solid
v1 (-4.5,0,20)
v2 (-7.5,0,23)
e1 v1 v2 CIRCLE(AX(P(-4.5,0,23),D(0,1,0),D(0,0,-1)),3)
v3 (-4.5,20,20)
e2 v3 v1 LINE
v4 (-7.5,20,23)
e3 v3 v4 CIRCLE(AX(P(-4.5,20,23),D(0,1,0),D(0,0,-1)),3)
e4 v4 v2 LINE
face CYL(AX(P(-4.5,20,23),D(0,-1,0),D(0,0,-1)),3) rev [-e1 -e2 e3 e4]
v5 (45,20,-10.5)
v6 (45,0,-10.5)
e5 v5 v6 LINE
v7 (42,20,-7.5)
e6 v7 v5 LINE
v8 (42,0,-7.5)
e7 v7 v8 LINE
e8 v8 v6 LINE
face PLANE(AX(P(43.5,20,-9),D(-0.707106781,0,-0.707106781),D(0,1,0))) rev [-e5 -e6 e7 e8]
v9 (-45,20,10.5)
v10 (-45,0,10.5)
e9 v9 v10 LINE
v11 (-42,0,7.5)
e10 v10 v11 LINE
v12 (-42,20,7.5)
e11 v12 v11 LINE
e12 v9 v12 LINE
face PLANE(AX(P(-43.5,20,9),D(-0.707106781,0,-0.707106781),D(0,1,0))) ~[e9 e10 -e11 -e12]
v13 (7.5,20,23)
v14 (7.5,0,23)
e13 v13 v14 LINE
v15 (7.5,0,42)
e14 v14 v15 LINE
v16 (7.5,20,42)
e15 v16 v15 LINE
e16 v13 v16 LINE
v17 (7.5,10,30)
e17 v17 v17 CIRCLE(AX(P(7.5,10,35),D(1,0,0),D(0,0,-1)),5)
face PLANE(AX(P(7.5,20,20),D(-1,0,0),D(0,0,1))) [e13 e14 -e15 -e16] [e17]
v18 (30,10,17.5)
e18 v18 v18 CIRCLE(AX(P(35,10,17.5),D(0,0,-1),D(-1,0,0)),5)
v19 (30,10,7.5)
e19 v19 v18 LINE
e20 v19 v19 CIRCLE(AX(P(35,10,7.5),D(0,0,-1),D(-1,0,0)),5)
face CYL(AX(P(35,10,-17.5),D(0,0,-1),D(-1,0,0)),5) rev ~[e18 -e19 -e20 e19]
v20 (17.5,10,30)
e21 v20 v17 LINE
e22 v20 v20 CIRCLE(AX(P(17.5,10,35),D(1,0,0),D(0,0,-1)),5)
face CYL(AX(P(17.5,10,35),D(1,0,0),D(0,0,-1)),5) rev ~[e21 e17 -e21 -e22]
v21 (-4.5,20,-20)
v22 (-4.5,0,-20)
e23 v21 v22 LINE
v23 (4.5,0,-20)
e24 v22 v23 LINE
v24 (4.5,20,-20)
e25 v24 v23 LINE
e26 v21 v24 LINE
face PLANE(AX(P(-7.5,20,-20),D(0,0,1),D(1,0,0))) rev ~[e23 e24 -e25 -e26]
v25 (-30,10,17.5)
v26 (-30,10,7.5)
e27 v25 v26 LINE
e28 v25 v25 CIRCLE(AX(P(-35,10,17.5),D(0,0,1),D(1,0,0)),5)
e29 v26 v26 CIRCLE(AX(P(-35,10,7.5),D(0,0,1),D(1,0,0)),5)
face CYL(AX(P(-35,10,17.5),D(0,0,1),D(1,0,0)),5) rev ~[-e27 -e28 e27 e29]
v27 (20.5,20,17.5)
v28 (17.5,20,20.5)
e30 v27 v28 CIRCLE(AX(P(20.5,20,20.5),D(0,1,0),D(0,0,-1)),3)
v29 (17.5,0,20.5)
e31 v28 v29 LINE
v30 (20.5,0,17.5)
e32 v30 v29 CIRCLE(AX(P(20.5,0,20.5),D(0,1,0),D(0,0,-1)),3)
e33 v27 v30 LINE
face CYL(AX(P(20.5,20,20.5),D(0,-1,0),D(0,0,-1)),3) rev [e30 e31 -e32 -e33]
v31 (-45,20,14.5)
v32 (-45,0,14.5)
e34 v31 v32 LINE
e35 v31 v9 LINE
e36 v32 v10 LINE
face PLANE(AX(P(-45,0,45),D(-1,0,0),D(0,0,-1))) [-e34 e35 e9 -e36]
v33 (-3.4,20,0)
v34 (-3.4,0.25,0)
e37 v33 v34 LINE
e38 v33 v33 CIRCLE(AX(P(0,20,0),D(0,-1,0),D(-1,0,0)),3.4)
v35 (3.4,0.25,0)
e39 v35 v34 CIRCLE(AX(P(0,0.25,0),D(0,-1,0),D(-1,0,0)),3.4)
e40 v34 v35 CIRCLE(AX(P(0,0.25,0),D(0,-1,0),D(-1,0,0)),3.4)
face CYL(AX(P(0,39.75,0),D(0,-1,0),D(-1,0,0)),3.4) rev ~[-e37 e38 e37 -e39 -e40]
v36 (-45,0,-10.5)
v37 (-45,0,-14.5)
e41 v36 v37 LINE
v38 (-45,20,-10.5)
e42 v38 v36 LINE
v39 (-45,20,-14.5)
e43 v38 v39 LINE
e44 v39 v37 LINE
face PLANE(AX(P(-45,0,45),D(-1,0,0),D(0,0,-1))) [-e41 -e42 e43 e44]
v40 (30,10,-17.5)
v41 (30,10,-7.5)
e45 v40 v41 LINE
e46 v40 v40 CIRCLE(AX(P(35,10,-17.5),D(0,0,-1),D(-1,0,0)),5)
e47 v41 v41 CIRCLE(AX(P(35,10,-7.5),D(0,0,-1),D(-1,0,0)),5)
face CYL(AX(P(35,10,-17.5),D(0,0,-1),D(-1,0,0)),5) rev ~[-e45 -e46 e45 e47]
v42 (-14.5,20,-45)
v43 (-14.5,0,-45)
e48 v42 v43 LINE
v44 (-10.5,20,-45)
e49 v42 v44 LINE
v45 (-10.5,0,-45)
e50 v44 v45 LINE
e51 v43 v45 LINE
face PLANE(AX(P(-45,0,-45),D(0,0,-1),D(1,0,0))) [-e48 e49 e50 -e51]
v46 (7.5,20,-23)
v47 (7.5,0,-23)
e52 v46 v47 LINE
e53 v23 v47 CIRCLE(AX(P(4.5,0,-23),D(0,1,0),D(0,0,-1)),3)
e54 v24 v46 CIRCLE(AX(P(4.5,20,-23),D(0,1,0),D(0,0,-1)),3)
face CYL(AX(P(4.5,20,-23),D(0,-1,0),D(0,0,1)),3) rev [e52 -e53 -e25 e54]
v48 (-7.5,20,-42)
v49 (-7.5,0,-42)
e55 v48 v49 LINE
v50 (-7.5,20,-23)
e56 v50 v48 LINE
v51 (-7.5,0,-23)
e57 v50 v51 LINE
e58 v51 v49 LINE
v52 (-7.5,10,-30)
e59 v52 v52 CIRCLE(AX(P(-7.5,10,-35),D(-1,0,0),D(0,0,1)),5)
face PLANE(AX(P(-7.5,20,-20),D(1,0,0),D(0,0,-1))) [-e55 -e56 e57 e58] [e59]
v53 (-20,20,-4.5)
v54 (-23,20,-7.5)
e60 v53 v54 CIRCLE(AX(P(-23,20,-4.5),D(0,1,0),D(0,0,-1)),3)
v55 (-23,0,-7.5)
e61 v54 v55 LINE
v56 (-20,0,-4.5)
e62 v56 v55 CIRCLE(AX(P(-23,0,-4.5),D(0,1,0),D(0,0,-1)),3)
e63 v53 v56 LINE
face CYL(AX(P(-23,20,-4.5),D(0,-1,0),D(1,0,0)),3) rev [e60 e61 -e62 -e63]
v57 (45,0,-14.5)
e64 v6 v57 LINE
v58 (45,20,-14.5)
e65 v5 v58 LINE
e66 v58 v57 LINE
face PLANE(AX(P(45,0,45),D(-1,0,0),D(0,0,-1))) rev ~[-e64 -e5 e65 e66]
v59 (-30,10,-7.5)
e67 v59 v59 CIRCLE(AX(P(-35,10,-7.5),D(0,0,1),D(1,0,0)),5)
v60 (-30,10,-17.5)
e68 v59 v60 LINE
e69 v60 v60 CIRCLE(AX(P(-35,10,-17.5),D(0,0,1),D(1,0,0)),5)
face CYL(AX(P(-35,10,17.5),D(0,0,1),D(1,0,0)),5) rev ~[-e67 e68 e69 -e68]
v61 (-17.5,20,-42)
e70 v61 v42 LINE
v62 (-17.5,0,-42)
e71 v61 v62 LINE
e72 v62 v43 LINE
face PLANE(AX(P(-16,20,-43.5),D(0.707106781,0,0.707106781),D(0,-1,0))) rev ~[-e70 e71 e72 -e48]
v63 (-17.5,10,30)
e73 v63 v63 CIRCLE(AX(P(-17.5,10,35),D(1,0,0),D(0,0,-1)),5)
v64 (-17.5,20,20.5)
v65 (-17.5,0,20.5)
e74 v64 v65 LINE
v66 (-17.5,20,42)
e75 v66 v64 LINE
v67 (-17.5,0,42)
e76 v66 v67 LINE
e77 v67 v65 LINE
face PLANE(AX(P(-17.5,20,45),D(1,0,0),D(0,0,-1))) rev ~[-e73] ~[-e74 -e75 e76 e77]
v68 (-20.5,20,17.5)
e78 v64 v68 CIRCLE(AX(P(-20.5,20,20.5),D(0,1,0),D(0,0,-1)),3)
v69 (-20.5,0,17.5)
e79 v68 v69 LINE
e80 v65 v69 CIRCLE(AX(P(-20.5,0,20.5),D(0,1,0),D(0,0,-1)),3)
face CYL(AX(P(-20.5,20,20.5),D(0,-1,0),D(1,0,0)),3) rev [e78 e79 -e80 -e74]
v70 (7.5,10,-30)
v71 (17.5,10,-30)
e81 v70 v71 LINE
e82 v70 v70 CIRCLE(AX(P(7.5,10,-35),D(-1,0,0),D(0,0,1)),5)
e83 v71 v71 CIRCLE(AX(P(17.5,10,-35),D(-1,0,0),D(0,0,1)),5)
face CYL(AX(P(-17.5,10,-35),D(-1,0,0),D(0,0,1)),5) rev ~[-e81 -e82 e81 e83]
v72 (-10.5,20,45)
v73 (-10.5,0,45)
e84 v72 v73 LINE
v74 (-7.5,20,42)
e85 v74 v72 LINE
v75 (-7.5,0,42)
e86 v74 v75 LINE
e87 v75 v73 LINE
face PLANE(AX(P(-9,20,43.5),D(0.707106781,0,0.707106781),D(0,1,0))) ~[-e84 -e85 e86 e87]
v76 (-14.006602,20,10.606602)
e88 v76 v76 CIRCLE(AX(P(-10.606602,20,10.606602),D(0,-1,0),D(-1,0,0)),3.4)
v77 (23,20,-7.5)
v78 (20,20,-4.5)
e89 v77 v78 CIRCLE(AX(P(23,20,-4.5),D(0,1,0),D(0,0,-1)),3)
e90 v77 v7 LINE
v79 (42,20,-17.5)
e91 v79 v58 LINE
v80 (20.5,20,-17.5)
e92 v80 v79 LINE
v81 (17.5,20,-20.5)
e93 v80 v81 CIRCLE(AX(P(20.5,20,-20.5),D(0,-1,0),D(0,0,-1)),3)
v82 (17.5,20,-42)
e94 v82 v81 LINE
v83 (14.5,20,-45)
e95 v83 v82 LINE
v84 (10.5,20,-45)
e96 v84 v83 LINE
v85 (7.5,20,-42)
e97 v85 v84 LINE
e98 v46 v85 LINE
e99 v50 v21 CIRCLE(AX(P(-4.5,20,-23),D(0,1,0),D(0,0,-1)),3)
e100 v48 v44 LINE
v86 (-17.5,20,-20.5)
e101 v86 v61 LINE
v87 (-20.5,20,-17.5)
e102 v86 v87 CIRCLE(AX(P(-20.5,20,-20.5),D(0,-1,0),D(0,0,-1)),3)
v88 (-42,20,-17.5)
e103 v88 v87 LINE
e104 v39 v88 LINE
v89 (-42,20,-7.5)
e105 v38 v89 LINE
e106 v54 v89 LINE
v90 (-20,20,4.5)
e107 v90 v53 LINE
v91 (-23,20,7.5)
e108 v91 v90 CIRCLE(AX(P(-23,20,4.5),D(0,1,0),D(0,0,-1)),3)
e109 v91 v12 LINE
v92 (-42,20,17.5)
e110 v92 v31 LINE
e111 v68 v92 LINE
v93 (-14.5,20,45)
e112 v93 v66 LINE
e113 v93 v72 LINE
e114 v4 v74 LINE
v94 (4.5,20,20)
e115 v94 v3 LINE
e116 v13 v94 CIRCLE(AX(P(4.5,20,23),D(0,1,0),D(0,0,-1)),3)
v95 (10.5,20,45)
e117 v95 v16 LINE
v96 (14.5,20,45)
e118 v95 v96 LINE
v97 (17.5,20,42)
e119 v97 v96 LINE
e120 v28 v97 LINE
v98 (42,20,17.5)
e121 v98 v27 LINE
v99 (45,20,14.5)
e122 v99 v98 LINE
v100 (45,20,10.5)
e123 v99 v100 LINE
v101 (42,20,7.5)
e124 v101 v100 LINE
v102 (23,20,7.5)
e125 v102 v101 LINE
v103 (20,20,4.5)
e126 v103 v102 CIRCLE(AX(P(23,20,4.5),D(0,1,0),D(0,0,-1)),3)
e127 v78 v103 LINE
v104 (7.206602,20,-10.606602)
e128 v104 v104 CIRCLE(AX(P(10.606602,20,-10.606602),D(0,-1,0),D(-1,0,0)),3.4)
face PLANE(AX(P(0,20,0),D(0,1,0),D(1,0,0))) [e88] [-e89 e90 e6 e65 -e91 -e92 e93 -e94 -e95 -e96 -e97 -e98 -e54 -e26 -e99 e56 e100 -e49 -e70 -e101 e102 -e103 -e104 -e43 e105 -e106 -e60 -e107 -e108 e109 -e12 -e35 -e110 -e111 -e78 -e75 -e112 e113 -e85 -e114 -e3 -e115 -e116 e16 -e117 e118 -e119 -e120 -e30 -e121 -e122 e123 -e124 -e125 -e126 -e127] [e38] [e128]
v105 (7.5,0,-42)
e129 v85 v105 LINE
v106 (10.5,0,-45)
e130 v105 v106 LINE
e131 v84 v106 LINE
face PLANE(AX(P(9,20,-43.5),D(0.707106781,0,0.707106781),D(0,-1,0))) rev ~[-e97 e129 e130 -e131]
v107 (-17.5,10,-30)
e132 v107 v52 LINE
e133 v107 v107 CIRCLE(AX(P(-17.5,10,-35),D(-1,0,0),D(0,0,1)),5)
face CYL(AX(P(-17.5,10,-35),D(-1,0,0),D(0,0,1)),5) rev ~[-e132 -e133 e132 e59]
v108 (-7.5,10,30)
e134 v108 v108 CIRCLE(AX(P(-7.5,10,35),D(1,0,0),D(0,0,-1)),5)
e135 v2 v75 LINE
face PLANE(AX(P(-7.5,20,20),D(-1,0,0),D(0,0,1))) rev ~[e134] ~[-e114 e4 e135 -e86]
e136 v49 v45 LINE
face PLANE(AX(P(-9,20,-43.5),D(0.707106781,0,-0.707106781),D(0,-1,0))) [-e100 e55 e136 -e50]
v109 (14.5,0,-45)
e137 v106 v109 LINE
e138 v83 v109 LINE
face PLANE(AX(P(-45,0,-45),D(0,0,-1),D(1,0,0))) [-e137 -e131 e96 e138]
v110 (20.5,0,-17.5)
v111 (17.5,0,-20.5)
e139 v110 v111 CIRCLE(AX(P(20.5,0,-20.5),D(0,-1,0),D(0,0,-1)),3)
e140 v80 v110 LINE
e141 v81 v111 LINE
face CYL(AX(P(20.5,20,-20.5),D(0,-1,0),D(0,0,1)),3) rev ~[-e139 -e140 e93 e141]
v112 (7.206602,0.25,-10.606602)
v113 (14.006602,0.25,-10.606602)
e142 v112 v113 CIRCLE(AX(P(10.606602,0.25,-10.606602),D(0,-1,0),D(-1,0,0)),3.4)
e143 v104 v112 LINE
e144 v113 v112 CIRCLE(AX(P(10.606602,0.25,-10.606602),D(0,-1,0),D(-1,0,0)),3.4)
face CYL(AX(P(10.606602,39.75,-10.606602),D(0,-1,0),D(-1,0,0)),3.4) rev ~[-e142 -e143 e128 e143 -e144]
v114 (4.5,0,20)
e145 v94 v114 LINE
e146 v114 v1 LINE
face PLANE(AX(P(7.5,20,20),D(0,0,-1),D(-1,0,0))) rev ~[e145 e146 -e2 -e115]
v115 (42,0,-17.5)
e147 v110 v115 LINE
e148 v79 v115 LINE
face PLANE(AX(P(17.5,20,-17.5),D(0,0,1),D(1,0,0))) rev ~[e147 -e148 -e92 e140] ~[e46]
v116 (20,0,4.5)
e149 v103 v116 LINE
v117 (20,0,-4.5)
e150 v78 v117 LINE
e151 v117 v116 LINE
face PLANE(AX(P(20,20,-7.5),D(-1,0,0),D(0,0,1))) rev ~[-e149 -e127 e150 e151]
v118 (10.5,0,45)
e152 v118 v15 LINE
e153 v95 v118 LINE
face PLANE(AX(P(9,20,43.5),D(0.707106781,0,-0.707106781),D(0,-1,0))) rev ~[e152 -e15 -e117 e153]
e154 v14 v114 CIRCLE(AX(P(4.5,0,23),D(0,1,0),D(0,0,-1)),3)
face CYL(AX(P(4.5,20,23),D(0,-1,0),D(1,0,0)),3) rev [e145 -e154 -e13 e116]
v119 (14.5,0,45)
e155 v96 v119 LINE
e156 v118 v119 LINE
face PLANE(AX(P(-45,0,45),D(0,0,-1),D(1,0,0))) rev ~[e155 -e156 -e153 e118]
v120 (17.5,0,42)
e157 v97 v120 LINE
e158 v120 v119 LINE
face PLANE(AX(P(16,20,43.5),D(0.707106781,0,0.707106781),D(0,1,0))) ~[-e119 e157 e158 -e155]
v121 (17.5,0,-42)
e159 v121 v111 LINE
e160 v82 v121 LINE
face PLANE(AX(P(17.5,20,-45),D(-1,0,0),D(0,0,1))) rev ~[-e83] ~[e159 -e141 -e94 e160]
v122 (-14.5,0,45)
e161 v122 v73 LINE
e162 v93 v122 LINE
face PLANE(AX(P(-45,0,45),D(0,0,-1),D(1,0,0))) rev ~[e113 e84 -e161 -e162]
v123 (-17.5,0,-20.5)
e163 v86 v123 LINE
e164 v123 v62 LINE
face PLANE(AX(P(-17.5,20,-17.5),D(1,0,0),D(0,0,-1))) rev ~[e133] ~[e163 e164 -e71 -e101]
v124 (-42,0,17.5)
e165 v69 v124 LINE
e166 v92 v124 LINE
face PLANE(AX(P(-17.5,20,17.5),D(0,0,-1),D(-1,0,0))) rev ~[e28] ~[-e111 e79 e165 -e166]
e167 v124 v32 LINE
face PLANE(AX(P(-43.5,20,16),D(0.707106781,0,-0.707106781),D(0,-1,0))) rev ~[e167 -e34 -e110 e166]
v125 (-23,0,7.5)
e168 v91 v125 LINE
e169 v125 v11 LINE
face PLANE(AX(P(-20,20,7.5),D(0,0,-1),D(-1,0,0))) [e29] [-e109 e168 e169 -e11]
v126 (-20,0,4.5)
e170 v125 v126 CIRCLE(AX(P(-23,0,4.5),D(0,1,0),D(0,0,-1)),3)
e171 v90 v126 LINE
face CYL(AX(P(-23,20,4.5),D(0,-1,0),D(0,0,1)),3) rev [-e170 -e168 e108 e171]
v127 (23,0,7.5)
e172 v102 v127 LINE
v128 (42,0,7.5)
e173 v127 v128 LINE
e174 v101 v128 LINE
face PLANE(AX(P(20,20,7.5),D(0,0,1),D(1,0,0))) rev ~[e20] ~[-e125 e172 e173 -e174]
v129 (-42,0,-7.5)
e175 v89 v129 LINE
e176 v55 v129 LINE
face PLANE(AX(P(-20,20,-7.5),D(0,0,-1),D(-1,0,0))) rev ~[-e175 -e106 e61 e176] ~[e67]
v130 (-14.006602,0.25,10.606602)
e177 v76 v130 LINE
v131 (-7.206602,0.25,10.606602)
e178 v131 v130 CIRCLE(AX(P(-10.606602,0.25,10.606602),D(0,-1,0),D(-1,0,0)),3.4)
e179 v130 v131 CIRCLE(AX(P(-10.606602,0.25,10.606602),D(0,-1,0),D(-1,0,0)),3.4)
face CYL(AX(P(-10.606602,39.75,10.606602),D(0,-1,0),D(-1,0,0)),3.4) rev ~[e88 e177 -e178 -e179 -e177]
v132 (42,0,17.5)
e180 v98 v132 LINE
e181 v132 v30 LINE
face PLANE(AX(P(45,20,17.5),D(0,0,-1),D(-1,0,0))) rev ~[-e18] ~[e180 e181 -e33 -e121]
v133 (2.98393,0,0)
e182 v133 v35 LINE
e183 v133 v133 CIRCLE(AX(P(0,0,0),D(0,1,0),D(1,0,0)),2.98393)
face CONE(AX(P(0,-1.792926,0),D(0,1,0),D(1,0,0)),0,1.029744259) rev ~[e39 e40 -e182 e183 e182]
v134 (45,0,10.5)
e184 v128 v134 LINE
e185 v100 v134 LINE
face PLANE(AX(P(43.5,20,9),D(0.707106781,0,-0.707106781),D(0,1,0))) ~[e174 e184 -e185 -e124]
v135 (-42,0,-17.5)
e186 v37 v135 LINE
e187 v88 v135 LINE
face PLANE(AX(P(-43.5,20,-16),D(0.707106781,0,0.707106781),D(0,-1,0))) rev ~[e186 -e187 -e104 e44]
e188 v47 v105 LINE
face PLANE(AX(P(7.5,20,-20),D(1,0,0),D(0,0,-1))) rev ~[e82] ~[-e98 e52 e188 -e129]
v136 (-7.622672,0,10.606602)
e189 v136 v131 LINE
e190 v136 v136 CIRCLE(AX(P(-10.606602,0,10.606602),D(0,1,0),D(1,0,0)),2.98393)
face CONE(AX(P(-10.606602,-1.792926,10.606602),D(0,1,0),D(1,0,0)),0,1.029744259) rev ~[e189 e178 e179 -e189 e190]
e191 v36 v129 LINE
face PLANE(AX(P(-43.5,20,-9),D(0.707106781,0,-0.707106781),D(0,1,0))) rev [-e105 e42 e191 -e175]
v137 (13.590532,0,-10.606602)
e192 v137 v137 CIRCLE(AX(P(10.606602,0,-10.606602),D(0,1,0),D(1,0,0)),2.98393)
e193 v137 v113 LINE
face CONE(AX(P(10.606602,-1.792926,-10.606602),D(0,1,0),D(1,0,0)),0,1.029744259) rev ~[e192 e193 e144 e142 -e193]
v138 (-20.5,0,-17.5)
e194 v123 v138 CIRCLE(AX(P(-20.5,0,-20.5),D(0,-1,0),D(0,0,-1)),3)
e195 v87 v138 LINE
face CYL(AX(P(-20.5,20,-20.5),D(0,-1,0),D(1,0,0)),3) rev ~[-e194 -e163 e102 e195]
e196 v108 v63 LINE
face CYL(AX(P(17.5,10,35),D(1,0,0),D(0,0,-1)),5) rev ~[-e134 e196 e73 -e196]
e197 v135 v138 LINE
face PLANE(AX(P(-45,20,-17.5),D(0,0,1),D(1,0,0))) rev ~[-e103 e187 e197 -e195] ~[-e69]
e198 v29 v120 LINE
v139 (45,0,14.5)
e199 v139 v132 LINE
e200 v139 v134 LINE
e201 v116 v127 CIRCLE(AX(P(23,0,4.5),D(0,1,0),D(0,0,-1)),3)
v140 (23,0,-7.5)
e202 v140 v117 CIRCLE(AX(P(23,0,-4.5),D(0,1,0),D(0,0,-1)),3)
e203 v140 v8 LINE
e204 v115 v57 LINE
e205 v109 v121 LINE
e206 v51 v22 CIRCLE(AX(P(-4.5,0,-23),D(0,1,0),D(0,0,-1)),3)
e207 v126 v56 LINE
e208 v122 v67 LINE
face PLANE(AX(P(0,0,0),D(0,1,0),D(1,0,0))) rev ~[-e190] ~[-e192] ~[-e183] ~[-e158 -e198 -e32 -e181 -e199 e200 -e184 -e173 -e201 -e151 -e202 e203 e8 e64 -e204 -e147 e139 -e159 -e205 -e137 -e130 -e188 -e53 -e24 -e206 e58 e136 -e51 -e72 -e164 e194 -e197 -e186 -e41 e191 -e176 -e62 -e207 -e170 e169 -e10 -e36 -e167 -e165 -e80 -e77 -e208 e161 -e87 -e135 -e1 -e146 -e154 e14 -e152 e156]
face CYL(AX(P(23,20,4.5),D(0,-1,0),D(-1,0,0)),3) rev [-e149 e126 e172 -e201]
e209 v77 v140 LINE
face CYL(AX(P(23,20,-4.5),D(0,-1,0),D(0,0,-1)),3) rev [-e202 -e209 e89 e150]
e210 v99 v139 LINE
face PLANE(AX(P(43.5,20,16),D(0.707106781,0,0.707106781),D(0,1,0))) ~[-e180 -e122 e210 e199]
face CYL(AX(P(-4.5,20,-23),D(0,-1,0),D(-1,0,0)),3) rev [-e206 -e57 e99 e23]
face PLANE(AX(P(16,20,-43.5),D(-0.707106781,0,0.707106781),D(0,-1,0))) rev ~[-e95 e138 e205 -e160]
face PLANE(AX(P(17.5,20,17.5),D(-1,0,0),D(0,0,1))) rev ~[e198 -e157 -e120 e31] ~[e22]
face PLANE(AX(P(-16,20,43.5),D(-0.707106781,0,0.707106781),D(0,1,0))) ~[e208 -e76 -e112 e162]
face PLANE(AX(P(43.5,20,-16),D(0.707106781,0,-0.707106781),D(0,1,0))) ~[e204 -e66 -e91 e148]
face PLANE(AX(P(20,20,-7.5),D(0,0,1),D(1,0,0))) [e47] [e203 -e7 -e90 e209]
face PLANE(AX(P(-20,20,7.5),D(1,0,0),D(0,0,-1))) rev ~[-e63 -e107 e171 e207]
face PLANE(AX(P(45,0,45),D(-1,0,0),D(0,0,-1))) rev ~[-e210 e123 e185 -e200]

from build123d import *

# Parameters (mm, degrees)
SKETCH1_W                = 90
SKETCH1_H                = 90
BOSS_EXTRUDE1_DEPTH      = 20
CHAMFER1_SIZE            = 3
M8_TAPPED_HOLE1_D        = 6.8
M8_TAPPED_HOLE1_DEPTH    = 19.75
M8_TAPPED_HOLE1_TIP      = 2.042926105
SKETCH4_W                = 15
SKETCH4_H                = 25
CUT_EXTRUDE1_DEPTH       = 42
FILLET1_R                = 3
CHAMFER2_SIZE            = 3
CIRPATTERN2_COUNT        = 4
FILLET1_OF_CIRPATTERN2_R = 3
CHAMFER3_SIZE            = 3
SKETCH5_W                = 27.5
SKETCH5_H                = 27.5
CUT_EXTRUDE2_DEPTH       = 42
CIRPATTERN3_COUNT        = 4
CHAMFER4_SIZE            = 3
FILLET2_R                = 3
SKETCH6_R                = 5
CUT_EXTRUDE3_DEPTH       = 42
CIRPATTERN4_COUNT        = 4
M8_TAPPED_HOLE2_D        = 6.8
M8_TAPPED_HOLE2_DEPTH    = 19.75
M8_TAPPED_HOLE2_TIP      = 2.042926105


with BuildPart() as part:
    # Sketch1 → Boss-Extrude1 (new body)
    with BuildSketch(Plane(origin=(0, 0, 0), x_dir=(1, 0, 0), z_dir=(0, 1, 0))):
        Rectangle(SKETCH1_W, SKETCH1_H)
    extrude(amount=BOSS_EXTRUDE1_DEPTH)

    # Chamfer1
    chamfer1_edges = [part.edges().sort_by_distance(p)[0] for p in [
        (-45, 10, -45),
        (45, 10, -45),
        (45, 10, 45),
        (-45, 10, 45),
    ]]
    chamfer(chamfer1_edges, length=CHAMFER1_SIZE)

    # M8 Tapped Hole1
    with Locations(Plane(origin=(0, 20, 0), x_dir=(1, 0, 0), z_dir=(0, 1, 0))):
        with Locations((0, 0)):
            Hole(M8_TAPPED_HOLE1_D / 2, depth=M8_TAPPED_HOLE1_DEPTH)
            with Locations((0, 0, -(M8_TAPPED_HOLE1_DEPTH + M8_TAPPED_HOLE1_TIP / 2))):  # 118° drill point
                Cone(0, M8_TAPPED_HOLE1_D / 2, M8_TAPPED_HOLE1_TIP, mode=Mode.SUBTRACT)

    # Sketch4 → Cut-Extrude1 (cut)
    with BuildSketch(Plane(origin=(0, 20, 0), x_dir=(1, 0, 0), z_dir=(0, 1, 0))):
        with Locations((0, 32.5)):
            Rectangle(SKETCH4_W, SKETCH4_H)
    cut_extrude1 = extrude(amount=-CUT_EXTRUDE1_DEPTH, mode=Mode.SUBTRACT)

    # Fillet1
    fillet1_edges = [part.edges().sort_by_distance(p)[0] for p in [
        (7.5, 10, -20),
        (-7.5, 10, -20),
    ]]
    fillet(fillet1_edges, radius=FILLET1_R)

    # Chamfer2
    chamfer2_edges = [part.edges().sort_by_distance(p)[0] for p in [
        (7.5, 10, -45),
        (-7.5, 10, -45),
    ]]
    chamfer(chamfer2_edges, length=CHAMFER2_SIZE)

    # CirPattern2: Cut-Extrude1 ×4 about axis
    cirpattern2_axis = Axis((0, 0, 0), (0, 1, 0))
    for i in range(1, CIRPATTERN2_COUNT):
        add(cut_extrude1.rotate(cirpattern2_axis, i * 360 / CIRPATTERN2_COUNT), mode=Mode.SUBTRACT)

    # Fillet1 of CirPattern2
    fillet1_of_cirpattern2_edges = [part.edges().sort_by_distance(p)[0] for p in [
        (-20, 10, -7.5),
        (-20, 10, 7.5),
        (-7.5, 10, 20),
        (7.5, 10, 20),
        (20, 10, 7.5),
        (20, 10, -7.5),
    ]]
    fillet(fillet1_of_cirpattern2_edges, radius=FILLET1_OF_CIRPATTERN2_R)

    # Chamfer3
    chamfer3_edges = [part.edges().sort_by_distance(p)[0] for p in [
        (-45, 10, -7.5),
        (-45, 10, 7.5),
        (-7.5, 10, 45),
        (7.5, 10, 45),
        (45, 10, 7.5),
        (45, 10, -7.5),
    ]]
    chamfer(chamfer3_edges, length=CHAMFER3_SIZE)

    # Sketch5 → Cut-Extrude2 (cut)
    with BuildSketch(Plane(origin=(0, 20, 0), x_dir=(1, 0, 0), z_dir=(0, 1, 0))):
        with Locations((-31.25, 31.25)):
            Rectangle(SKETCH5_W, SKETCH5_H)
    cut_extrude2 = extrude(amount=-CUT_EXTRUDE2_DEPTH, mode=Mode.SUBTRACT)

    # CirPattern3: Cut-Extrude2 ×4 about axis
    cirpattern3_axis = Axis((0, 0, 0), (0, 1, 0))
    for i in range(1, CIRPATTERN3_COUNT):
        add(cut_extrude2.rotate(cirpattern3_axis, i * 360 / CIRPATTERN3_COUNT), mode=Mode.SUBTRACT)

    # Chamfer4
    chamfer4_edges = [part.edges().sort_by_distance(p)[0] for p in [
        (-17.5, 10, -45),
        (-45, 10, -17.5),
        (-45, 10, 17.5),
        (-17.5, 10, 45),
        (17.5, 10, 45),
        (45, 10, 17.5),
        (45, 10, -17.5),
        (17.5, 10, -45),
    ]]
    chamfer(chamfer4_edges, length=CHAMFER4_SIZE)

    # Fillet2
    fillet2_edges = [part.edges().sort_by_distance(p)[0] for p in [
        (-17.5, 10, -17.5),
        (-17.5, 10, 17.5),
        (17.5, 10, 17.5),
        (17.5, 10, -17.5),
    ]]
    fillet(fillet2_edges, radius=FILLET2_R)

    # Sketch6 → Cut-Extrude3 (cut)
    with BuildSketch(Plane.ZY.offset(17.5)):
        with Locations((-35, 10)):
            Circle(SKETCH6_R)
    cut_extrude3 = extrude(amount=-CUT_EXTRUDE3_DEPTH, mode=Mode.SUBTRACT)

    # CirPattern4: Cut-Extrude3 ×4 about axis
    cirpattern4_axis = Axis((0, 20, 0), (0, 1, 0))
    for i in range(1, CIRPATTERN4_COUNT):
        add(cut_extrude3.rotate(cirpattern4_axis, i * 360 / CIRPATTERN4_COUNT), mode=Mode.SUBTRACT)

    # M8 Tapped Hole2
    with Locations(Plane(origin=(0, 20, 0), x_dir=(1, 0, 0), z_dir=(0, 1, 0))):
        with Locations((-10.606601718, -10.606601718), (10.606601718, 10.606601718)):
            Hole(M8_TAPPED_HOLE2_D / 2, depth=M8_TAPPED_HOLE2_DEPTH)
            with Locations((0, 0, -(M8_TAPPED_HOLE2_DEPTH + M8_TAPPED_HOLE2_TIP / 2))):  # 118° drill point
                Cone(0, M8_TAPPED_HOLE2_D / 2, M8_TAPPED_HOLE2_TIP, mode=Mode.SUBTRACT)


solid = part.part
